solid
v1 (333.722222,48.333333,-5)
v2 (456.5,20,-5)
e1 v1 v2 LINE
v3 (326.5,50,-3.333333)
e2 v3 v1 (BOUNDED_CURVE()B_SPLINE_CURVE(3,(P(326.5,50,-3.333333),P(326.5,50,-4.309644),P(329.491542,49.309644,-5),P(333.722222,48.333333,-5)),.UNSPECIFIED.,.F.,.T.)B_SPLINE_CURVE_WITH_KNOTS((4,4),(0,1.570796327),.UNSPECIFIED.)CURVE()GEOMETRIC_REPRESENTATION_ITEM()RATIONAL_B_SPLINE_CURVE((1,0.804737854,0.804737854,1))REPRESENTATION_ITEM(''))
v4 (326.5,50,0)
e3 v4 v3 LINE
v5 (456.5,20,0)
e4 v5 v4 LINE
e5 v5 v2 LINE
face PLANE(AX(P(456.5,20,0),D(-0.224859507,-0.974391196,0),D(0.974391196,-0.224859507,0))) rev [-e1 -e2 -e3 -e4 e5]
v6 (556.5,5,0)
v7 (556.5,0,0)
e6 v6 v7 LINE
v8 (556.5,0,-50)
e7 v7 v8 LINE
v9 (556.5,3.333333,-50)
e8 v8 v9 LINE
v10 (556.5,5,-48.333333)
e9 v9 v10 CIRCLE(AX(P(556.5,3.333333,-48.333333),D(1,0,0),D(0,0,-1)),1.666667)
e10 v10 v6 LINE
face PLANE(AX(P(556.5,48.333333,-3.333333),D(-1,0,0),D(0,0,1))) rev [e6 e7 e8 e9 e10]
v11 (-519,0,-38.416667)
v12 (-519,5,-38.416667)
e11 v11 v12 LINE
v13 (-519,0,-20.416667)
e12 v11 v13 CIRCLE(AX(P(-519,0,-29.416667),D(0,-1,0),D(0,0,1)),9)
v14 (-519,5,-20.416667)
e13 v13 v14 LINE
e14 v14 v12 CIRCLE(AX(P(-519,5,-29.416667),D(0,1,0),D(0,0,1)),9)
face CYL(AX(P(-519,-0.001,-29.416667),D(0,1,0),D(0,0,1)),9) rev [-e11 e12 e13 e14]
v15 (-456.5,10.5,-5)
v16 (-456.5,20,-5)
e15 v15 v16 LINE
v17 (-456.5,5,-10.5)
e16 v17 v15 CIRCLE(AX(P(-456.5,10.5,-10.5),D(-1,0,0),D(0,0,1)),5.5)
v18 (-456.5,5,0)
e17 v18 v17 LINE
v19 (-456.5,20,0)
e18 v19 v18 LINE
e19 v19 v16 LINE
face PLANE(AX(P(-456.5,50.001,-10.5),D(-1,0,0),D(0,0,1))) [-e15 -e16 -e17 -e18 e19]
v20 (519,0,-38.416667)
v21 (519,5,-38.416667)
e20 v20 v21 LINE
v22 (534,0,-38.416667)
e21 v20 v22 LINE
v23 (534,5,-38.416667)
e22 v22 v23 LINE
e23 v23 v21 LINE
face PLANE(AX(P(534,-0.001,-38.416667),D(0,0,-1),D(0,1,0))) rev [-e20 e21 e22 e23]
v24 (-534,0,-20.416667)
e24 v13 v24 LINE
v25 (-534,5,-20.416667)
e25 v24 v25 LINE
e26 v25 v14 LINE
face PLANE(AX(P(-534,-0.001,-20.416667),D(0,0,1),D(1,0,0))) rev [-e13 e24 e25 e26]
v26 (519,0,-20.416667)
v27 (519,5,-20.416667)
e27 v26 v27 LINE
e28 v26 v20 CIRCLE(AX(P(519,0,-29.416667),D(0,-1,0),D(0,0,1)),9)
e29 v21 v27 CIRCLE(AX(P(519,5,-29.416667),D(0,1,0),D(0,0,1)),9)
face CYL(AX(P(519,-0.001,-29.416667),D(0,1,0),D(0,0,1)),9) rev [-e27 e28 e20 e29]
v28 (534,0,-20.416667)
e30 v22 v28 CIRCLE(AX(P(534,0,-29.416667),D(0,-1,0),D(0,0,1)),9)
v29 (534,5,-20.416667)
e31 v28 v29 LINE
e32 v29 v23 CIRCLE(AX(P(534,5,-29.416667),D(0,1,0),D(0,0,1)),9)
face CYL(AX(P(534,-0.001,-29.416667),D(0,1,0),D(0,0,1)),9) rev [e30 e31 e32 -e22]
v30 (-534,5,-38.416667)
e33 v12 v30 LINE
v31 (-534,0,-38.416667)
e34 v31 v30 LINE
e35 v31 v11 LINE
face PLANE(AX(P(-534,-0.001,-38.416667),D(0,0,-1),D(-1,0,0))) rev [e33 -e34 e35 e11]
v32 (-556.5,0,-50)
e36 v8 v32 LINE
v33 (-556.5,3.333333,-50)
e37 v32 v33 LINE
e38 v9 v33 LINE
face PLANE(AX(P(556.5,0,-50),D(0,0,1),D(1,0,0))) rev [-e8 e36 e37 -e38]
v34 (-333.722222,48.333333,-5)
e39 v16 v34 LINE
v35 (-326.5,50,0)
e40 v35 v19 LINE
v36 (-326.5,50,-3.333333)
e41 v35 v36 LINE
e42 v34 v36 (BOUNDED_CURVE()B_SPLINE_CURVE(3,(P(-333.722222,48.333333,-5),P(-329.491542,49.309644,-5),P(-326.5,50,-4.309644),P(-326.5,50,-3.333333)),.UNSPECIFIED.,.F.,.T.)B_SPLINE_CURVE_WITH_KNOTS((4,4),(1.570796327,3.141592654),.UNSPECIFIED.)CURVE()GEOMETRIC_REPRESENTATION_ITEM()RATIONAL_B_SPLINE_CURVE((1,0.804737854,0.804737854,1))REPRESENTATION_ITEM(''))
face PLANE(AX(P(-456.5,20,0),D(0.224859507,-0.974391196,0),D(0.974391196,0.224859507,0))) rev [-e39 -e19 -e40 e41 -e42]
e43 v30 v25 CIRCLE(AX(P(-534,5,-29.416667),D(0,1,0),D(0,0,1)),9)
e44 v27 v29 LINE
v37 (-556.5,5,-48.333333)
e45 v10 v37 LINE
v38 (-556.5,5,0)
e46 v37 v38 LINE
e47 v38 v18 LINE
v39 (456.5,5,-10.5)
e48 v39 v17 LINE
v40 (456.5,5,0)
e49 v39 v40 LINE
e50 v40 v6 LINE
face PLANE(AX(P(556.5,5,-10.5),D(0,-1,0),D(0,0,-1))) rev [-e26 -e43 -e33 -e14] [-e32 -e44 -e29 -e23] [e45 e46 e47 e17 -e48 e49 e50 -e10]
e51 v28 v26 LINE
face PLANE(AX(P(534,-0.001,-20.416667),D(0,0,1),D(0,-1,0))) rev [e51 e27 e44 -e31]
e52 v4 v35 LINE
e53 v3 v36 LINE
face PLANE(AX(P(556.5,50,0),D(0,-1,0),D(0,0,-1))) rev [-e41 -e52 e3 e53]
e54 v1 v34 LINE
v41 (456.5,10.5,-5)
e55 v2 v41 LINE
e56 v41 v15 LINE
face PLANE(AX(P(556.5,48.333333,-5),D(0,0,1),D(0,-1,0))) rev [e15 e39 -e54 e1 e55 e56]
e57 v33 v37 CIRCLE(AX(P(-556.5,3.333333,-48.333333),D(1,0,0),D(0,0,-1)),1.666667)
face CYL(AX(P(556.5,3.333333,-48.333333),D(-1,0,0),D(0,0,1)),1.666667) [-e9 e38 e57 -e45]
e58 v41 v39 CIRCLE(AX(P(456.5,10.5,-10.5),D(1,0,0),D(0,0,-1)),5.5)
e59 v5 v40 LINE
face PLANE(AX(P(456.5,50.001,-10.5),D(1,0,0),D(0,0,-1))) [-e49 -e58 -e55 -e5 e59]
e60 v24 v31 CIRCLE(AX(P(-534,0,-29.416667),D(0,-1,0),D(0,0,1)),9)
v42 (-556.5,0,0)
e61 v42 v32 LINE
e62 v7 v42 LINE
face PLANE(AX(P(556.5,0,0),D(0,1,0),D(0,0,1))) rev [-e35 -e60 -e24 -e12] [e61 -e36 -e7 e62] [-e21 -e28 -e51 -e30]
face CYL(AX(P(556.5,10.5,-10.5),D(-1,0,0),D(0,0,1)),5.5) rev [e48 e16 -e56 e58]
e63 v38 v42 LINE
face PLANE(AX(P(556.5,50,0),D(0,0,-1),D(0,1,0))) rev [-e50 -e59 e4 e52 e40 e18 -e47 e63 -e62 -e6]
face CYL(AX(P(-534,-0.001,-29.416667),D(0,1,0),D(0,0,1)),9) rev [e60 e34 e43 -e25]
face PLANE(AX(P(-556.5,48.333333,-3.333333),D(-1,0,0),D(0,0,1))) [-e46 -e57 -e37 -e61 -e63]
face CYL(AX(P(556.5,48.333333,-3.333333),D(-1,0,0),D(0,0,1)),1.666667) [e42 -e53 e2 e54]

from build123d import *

# Parameters (mm, degrees)
HOT_ROLLED_EQUAL_LEG_ANGLE_STEEL_GB_T97_DEPTH = 1113
CUT_EXTRUDE1_REACH                            = 562.551
CUT_EXTRUDE2_REACH                            = 562.551
SKETCH16_W                                    = 100
SKETCH16_H                                    = 10.5
CUT_EXTRUDE3_DEPTH                            = 561.550845151
CUT_EXTRUDE3_DEPTH_BACK                       = 561.550845151


with BuildPart() as part:
    # Sketch11 → Hot-rolled equal-leg angle steel (gb t9787-1988) 50×5(1) (new body)
    with BuildSketch(Plane.YZ.offset(-556.5)):
        with BuildLine():
            Line((50, 0), (0, 0))
            Line((0, 0), (0, -50))
            Line((0, -50), (3.333333333, -50))
            ThreePointArc((3.333333333, -50), (4.511844635, -49.511844635), (5, -48.333333333))
            Line((5, -48.333333333), (5, -10.5))
            ThreePointArc((5, -10.5), (6.610912703, -6.610912703), (10.5, -5))
            Line((10.5, -5), (48.333333333, -5))
            ThreePointArc((48.333333333, -5), (49.511844635, -4.511844635), (50, -3.333333333))
            Line((50, -3.333333333), (50, 0))
        make_face()
    extrude(amount=HOT_ROLLED_EQUAL_LEG_ANGLE_STEEL_GB_T97_DEPTH)

    # Sketch13 → Cut-Extrude1 (cut, up to next)
    with BuildSketch(Plane(origin=(0, 5, 0), x_dir=(1, 0, 0), z_dir=(0, 1, 0)), mode=Mode.PRIVATE) as cut_extrude1_sk1:
        with BuildLine():
            Line((-534, 38.416666667), (-519, 38.416666667))
            ThreePointArc((-519, 38.416666667), (-510, 29.416666667), (-519, 20.416666667))
            Line((-519, 20.416666667), (-534, 20.416666667))
            ThreePointArc((-534, 20.416666667), (-543, 29.416666667), (-534, 38.416666667))
        make_face()
    cut_extrude1_tool1 = extrude(cut_extrude1_sk1.sketch, amount=-CUT_EXTRUDE1_REACH, mode=Mode.PRIVATE) & part.part
    # Sketch13 → Cut-Extrude1 (cut, up to next)
    with BuildSketch(Plane(origin=(0, 5, 0), x_dir=(1, 0, 0), z_dir=(0, 1, 0)), mode=Mode.PRIVATE) as cut_extrude1_sk2:
        with BuildLine():
            Line((534, 20.416666667), (519, 20.416666667))
            ThreePointArc((519, 20.416666667), (510, 29.416666667), (519, 38.416666667))
            Line((519, 38.416666667), (534, 38.416666667))
            ThreePointArc((534, 38.416666667), (543, 29.416666667), (534, 20.416666667))
        make_face()
    cut_extrude1_tool2 = extrude(cut_extrude1_sk2.sketch, amount=-CUT_EXTRUDE1_REACH, mode=Mode.PRIVATE) & part.part
    add(cut_extrude1_tool1.solids().sort_by_distance((-526.5, 5, -29.416667))[0], mode=Mode.SUBTRACT)
    add(cut_extrude1_tool2.solids().sort_by_distance((526.5, 5, -29.416667))[0], mode=Mode.SUBTRACT)

    # Sketch16 → Cut-Extrude2 (cut, up to next)
    with BuildSketch(Plane(origin=(0, 5, 0), x_dir=(1, 0, 0), z_dir=(0, 1, 0)), mode=Mode.PRIVATE) as cut_extrude2_sk1:
        with Locations((506.5, 5.25)):
            Rectangle(SKETCH16_W, SKETCH16_H)
    cut_extrude2_tool1 = extrude(cut_extrude2_sk1.sketch, amount=CUT_EXTRUDE2_REACH, mode=Mode.PRIVATE) & part.part
    # Sketch16 → Cut-Extrude2 (cut, up to next)
    with BuildSketch(Plane(origin=(0, 5, 0), x_dir=(1, 0, 0), z_dir=(0, 1, 0)), mode=Mode.PRIVATE) as cut_extrude2_sk2:
        with Locations((-506.5, 5.25)):
            Rectangle(SKETCH16_W, SKETCH16_H)
    cut_extrude2_tool2 = extrude(cut_extrude2_sk2.sketch, amount=CUT_EXTRUDE2_REACH, mode=Mode.PRIVATE) & part.part
    add(cut_extrude2_tool1.solids().sort_by_distance((506.5, 5, -5.25))[0], mode=Mode.SUBTRACT)
    add(cut_extrude2_tool2.solids().sort_by_distance((-506.5, 5, -5.25))[0], mode=Mode.SUBTRACT)

    # Sketch17 → Cut-Extrude3 (cut, two sides: drawn at the far end of the back side and taken through both)
    with BuildSketch(Plane(origin=(0, 0, -5), x_dir=(-1, 0, 0), z_dir=(0, 0, -1)).offset(-CUT_EXTRUDE3_DEPTH_BACK)):
        Polygon((326.5, 50), (456.5, 50), (456.5, 20), align=None)
        Polygon((-456.5, 20), (-326.5, 50), (-456.5, 50), align=None)
    extrude(amount=CUT_EXTRUDE3_DEPTH + CUT_EXTRUDE3_DEPTH_BACK, mode=Mode.SUBTRACT)


solid = part.part
